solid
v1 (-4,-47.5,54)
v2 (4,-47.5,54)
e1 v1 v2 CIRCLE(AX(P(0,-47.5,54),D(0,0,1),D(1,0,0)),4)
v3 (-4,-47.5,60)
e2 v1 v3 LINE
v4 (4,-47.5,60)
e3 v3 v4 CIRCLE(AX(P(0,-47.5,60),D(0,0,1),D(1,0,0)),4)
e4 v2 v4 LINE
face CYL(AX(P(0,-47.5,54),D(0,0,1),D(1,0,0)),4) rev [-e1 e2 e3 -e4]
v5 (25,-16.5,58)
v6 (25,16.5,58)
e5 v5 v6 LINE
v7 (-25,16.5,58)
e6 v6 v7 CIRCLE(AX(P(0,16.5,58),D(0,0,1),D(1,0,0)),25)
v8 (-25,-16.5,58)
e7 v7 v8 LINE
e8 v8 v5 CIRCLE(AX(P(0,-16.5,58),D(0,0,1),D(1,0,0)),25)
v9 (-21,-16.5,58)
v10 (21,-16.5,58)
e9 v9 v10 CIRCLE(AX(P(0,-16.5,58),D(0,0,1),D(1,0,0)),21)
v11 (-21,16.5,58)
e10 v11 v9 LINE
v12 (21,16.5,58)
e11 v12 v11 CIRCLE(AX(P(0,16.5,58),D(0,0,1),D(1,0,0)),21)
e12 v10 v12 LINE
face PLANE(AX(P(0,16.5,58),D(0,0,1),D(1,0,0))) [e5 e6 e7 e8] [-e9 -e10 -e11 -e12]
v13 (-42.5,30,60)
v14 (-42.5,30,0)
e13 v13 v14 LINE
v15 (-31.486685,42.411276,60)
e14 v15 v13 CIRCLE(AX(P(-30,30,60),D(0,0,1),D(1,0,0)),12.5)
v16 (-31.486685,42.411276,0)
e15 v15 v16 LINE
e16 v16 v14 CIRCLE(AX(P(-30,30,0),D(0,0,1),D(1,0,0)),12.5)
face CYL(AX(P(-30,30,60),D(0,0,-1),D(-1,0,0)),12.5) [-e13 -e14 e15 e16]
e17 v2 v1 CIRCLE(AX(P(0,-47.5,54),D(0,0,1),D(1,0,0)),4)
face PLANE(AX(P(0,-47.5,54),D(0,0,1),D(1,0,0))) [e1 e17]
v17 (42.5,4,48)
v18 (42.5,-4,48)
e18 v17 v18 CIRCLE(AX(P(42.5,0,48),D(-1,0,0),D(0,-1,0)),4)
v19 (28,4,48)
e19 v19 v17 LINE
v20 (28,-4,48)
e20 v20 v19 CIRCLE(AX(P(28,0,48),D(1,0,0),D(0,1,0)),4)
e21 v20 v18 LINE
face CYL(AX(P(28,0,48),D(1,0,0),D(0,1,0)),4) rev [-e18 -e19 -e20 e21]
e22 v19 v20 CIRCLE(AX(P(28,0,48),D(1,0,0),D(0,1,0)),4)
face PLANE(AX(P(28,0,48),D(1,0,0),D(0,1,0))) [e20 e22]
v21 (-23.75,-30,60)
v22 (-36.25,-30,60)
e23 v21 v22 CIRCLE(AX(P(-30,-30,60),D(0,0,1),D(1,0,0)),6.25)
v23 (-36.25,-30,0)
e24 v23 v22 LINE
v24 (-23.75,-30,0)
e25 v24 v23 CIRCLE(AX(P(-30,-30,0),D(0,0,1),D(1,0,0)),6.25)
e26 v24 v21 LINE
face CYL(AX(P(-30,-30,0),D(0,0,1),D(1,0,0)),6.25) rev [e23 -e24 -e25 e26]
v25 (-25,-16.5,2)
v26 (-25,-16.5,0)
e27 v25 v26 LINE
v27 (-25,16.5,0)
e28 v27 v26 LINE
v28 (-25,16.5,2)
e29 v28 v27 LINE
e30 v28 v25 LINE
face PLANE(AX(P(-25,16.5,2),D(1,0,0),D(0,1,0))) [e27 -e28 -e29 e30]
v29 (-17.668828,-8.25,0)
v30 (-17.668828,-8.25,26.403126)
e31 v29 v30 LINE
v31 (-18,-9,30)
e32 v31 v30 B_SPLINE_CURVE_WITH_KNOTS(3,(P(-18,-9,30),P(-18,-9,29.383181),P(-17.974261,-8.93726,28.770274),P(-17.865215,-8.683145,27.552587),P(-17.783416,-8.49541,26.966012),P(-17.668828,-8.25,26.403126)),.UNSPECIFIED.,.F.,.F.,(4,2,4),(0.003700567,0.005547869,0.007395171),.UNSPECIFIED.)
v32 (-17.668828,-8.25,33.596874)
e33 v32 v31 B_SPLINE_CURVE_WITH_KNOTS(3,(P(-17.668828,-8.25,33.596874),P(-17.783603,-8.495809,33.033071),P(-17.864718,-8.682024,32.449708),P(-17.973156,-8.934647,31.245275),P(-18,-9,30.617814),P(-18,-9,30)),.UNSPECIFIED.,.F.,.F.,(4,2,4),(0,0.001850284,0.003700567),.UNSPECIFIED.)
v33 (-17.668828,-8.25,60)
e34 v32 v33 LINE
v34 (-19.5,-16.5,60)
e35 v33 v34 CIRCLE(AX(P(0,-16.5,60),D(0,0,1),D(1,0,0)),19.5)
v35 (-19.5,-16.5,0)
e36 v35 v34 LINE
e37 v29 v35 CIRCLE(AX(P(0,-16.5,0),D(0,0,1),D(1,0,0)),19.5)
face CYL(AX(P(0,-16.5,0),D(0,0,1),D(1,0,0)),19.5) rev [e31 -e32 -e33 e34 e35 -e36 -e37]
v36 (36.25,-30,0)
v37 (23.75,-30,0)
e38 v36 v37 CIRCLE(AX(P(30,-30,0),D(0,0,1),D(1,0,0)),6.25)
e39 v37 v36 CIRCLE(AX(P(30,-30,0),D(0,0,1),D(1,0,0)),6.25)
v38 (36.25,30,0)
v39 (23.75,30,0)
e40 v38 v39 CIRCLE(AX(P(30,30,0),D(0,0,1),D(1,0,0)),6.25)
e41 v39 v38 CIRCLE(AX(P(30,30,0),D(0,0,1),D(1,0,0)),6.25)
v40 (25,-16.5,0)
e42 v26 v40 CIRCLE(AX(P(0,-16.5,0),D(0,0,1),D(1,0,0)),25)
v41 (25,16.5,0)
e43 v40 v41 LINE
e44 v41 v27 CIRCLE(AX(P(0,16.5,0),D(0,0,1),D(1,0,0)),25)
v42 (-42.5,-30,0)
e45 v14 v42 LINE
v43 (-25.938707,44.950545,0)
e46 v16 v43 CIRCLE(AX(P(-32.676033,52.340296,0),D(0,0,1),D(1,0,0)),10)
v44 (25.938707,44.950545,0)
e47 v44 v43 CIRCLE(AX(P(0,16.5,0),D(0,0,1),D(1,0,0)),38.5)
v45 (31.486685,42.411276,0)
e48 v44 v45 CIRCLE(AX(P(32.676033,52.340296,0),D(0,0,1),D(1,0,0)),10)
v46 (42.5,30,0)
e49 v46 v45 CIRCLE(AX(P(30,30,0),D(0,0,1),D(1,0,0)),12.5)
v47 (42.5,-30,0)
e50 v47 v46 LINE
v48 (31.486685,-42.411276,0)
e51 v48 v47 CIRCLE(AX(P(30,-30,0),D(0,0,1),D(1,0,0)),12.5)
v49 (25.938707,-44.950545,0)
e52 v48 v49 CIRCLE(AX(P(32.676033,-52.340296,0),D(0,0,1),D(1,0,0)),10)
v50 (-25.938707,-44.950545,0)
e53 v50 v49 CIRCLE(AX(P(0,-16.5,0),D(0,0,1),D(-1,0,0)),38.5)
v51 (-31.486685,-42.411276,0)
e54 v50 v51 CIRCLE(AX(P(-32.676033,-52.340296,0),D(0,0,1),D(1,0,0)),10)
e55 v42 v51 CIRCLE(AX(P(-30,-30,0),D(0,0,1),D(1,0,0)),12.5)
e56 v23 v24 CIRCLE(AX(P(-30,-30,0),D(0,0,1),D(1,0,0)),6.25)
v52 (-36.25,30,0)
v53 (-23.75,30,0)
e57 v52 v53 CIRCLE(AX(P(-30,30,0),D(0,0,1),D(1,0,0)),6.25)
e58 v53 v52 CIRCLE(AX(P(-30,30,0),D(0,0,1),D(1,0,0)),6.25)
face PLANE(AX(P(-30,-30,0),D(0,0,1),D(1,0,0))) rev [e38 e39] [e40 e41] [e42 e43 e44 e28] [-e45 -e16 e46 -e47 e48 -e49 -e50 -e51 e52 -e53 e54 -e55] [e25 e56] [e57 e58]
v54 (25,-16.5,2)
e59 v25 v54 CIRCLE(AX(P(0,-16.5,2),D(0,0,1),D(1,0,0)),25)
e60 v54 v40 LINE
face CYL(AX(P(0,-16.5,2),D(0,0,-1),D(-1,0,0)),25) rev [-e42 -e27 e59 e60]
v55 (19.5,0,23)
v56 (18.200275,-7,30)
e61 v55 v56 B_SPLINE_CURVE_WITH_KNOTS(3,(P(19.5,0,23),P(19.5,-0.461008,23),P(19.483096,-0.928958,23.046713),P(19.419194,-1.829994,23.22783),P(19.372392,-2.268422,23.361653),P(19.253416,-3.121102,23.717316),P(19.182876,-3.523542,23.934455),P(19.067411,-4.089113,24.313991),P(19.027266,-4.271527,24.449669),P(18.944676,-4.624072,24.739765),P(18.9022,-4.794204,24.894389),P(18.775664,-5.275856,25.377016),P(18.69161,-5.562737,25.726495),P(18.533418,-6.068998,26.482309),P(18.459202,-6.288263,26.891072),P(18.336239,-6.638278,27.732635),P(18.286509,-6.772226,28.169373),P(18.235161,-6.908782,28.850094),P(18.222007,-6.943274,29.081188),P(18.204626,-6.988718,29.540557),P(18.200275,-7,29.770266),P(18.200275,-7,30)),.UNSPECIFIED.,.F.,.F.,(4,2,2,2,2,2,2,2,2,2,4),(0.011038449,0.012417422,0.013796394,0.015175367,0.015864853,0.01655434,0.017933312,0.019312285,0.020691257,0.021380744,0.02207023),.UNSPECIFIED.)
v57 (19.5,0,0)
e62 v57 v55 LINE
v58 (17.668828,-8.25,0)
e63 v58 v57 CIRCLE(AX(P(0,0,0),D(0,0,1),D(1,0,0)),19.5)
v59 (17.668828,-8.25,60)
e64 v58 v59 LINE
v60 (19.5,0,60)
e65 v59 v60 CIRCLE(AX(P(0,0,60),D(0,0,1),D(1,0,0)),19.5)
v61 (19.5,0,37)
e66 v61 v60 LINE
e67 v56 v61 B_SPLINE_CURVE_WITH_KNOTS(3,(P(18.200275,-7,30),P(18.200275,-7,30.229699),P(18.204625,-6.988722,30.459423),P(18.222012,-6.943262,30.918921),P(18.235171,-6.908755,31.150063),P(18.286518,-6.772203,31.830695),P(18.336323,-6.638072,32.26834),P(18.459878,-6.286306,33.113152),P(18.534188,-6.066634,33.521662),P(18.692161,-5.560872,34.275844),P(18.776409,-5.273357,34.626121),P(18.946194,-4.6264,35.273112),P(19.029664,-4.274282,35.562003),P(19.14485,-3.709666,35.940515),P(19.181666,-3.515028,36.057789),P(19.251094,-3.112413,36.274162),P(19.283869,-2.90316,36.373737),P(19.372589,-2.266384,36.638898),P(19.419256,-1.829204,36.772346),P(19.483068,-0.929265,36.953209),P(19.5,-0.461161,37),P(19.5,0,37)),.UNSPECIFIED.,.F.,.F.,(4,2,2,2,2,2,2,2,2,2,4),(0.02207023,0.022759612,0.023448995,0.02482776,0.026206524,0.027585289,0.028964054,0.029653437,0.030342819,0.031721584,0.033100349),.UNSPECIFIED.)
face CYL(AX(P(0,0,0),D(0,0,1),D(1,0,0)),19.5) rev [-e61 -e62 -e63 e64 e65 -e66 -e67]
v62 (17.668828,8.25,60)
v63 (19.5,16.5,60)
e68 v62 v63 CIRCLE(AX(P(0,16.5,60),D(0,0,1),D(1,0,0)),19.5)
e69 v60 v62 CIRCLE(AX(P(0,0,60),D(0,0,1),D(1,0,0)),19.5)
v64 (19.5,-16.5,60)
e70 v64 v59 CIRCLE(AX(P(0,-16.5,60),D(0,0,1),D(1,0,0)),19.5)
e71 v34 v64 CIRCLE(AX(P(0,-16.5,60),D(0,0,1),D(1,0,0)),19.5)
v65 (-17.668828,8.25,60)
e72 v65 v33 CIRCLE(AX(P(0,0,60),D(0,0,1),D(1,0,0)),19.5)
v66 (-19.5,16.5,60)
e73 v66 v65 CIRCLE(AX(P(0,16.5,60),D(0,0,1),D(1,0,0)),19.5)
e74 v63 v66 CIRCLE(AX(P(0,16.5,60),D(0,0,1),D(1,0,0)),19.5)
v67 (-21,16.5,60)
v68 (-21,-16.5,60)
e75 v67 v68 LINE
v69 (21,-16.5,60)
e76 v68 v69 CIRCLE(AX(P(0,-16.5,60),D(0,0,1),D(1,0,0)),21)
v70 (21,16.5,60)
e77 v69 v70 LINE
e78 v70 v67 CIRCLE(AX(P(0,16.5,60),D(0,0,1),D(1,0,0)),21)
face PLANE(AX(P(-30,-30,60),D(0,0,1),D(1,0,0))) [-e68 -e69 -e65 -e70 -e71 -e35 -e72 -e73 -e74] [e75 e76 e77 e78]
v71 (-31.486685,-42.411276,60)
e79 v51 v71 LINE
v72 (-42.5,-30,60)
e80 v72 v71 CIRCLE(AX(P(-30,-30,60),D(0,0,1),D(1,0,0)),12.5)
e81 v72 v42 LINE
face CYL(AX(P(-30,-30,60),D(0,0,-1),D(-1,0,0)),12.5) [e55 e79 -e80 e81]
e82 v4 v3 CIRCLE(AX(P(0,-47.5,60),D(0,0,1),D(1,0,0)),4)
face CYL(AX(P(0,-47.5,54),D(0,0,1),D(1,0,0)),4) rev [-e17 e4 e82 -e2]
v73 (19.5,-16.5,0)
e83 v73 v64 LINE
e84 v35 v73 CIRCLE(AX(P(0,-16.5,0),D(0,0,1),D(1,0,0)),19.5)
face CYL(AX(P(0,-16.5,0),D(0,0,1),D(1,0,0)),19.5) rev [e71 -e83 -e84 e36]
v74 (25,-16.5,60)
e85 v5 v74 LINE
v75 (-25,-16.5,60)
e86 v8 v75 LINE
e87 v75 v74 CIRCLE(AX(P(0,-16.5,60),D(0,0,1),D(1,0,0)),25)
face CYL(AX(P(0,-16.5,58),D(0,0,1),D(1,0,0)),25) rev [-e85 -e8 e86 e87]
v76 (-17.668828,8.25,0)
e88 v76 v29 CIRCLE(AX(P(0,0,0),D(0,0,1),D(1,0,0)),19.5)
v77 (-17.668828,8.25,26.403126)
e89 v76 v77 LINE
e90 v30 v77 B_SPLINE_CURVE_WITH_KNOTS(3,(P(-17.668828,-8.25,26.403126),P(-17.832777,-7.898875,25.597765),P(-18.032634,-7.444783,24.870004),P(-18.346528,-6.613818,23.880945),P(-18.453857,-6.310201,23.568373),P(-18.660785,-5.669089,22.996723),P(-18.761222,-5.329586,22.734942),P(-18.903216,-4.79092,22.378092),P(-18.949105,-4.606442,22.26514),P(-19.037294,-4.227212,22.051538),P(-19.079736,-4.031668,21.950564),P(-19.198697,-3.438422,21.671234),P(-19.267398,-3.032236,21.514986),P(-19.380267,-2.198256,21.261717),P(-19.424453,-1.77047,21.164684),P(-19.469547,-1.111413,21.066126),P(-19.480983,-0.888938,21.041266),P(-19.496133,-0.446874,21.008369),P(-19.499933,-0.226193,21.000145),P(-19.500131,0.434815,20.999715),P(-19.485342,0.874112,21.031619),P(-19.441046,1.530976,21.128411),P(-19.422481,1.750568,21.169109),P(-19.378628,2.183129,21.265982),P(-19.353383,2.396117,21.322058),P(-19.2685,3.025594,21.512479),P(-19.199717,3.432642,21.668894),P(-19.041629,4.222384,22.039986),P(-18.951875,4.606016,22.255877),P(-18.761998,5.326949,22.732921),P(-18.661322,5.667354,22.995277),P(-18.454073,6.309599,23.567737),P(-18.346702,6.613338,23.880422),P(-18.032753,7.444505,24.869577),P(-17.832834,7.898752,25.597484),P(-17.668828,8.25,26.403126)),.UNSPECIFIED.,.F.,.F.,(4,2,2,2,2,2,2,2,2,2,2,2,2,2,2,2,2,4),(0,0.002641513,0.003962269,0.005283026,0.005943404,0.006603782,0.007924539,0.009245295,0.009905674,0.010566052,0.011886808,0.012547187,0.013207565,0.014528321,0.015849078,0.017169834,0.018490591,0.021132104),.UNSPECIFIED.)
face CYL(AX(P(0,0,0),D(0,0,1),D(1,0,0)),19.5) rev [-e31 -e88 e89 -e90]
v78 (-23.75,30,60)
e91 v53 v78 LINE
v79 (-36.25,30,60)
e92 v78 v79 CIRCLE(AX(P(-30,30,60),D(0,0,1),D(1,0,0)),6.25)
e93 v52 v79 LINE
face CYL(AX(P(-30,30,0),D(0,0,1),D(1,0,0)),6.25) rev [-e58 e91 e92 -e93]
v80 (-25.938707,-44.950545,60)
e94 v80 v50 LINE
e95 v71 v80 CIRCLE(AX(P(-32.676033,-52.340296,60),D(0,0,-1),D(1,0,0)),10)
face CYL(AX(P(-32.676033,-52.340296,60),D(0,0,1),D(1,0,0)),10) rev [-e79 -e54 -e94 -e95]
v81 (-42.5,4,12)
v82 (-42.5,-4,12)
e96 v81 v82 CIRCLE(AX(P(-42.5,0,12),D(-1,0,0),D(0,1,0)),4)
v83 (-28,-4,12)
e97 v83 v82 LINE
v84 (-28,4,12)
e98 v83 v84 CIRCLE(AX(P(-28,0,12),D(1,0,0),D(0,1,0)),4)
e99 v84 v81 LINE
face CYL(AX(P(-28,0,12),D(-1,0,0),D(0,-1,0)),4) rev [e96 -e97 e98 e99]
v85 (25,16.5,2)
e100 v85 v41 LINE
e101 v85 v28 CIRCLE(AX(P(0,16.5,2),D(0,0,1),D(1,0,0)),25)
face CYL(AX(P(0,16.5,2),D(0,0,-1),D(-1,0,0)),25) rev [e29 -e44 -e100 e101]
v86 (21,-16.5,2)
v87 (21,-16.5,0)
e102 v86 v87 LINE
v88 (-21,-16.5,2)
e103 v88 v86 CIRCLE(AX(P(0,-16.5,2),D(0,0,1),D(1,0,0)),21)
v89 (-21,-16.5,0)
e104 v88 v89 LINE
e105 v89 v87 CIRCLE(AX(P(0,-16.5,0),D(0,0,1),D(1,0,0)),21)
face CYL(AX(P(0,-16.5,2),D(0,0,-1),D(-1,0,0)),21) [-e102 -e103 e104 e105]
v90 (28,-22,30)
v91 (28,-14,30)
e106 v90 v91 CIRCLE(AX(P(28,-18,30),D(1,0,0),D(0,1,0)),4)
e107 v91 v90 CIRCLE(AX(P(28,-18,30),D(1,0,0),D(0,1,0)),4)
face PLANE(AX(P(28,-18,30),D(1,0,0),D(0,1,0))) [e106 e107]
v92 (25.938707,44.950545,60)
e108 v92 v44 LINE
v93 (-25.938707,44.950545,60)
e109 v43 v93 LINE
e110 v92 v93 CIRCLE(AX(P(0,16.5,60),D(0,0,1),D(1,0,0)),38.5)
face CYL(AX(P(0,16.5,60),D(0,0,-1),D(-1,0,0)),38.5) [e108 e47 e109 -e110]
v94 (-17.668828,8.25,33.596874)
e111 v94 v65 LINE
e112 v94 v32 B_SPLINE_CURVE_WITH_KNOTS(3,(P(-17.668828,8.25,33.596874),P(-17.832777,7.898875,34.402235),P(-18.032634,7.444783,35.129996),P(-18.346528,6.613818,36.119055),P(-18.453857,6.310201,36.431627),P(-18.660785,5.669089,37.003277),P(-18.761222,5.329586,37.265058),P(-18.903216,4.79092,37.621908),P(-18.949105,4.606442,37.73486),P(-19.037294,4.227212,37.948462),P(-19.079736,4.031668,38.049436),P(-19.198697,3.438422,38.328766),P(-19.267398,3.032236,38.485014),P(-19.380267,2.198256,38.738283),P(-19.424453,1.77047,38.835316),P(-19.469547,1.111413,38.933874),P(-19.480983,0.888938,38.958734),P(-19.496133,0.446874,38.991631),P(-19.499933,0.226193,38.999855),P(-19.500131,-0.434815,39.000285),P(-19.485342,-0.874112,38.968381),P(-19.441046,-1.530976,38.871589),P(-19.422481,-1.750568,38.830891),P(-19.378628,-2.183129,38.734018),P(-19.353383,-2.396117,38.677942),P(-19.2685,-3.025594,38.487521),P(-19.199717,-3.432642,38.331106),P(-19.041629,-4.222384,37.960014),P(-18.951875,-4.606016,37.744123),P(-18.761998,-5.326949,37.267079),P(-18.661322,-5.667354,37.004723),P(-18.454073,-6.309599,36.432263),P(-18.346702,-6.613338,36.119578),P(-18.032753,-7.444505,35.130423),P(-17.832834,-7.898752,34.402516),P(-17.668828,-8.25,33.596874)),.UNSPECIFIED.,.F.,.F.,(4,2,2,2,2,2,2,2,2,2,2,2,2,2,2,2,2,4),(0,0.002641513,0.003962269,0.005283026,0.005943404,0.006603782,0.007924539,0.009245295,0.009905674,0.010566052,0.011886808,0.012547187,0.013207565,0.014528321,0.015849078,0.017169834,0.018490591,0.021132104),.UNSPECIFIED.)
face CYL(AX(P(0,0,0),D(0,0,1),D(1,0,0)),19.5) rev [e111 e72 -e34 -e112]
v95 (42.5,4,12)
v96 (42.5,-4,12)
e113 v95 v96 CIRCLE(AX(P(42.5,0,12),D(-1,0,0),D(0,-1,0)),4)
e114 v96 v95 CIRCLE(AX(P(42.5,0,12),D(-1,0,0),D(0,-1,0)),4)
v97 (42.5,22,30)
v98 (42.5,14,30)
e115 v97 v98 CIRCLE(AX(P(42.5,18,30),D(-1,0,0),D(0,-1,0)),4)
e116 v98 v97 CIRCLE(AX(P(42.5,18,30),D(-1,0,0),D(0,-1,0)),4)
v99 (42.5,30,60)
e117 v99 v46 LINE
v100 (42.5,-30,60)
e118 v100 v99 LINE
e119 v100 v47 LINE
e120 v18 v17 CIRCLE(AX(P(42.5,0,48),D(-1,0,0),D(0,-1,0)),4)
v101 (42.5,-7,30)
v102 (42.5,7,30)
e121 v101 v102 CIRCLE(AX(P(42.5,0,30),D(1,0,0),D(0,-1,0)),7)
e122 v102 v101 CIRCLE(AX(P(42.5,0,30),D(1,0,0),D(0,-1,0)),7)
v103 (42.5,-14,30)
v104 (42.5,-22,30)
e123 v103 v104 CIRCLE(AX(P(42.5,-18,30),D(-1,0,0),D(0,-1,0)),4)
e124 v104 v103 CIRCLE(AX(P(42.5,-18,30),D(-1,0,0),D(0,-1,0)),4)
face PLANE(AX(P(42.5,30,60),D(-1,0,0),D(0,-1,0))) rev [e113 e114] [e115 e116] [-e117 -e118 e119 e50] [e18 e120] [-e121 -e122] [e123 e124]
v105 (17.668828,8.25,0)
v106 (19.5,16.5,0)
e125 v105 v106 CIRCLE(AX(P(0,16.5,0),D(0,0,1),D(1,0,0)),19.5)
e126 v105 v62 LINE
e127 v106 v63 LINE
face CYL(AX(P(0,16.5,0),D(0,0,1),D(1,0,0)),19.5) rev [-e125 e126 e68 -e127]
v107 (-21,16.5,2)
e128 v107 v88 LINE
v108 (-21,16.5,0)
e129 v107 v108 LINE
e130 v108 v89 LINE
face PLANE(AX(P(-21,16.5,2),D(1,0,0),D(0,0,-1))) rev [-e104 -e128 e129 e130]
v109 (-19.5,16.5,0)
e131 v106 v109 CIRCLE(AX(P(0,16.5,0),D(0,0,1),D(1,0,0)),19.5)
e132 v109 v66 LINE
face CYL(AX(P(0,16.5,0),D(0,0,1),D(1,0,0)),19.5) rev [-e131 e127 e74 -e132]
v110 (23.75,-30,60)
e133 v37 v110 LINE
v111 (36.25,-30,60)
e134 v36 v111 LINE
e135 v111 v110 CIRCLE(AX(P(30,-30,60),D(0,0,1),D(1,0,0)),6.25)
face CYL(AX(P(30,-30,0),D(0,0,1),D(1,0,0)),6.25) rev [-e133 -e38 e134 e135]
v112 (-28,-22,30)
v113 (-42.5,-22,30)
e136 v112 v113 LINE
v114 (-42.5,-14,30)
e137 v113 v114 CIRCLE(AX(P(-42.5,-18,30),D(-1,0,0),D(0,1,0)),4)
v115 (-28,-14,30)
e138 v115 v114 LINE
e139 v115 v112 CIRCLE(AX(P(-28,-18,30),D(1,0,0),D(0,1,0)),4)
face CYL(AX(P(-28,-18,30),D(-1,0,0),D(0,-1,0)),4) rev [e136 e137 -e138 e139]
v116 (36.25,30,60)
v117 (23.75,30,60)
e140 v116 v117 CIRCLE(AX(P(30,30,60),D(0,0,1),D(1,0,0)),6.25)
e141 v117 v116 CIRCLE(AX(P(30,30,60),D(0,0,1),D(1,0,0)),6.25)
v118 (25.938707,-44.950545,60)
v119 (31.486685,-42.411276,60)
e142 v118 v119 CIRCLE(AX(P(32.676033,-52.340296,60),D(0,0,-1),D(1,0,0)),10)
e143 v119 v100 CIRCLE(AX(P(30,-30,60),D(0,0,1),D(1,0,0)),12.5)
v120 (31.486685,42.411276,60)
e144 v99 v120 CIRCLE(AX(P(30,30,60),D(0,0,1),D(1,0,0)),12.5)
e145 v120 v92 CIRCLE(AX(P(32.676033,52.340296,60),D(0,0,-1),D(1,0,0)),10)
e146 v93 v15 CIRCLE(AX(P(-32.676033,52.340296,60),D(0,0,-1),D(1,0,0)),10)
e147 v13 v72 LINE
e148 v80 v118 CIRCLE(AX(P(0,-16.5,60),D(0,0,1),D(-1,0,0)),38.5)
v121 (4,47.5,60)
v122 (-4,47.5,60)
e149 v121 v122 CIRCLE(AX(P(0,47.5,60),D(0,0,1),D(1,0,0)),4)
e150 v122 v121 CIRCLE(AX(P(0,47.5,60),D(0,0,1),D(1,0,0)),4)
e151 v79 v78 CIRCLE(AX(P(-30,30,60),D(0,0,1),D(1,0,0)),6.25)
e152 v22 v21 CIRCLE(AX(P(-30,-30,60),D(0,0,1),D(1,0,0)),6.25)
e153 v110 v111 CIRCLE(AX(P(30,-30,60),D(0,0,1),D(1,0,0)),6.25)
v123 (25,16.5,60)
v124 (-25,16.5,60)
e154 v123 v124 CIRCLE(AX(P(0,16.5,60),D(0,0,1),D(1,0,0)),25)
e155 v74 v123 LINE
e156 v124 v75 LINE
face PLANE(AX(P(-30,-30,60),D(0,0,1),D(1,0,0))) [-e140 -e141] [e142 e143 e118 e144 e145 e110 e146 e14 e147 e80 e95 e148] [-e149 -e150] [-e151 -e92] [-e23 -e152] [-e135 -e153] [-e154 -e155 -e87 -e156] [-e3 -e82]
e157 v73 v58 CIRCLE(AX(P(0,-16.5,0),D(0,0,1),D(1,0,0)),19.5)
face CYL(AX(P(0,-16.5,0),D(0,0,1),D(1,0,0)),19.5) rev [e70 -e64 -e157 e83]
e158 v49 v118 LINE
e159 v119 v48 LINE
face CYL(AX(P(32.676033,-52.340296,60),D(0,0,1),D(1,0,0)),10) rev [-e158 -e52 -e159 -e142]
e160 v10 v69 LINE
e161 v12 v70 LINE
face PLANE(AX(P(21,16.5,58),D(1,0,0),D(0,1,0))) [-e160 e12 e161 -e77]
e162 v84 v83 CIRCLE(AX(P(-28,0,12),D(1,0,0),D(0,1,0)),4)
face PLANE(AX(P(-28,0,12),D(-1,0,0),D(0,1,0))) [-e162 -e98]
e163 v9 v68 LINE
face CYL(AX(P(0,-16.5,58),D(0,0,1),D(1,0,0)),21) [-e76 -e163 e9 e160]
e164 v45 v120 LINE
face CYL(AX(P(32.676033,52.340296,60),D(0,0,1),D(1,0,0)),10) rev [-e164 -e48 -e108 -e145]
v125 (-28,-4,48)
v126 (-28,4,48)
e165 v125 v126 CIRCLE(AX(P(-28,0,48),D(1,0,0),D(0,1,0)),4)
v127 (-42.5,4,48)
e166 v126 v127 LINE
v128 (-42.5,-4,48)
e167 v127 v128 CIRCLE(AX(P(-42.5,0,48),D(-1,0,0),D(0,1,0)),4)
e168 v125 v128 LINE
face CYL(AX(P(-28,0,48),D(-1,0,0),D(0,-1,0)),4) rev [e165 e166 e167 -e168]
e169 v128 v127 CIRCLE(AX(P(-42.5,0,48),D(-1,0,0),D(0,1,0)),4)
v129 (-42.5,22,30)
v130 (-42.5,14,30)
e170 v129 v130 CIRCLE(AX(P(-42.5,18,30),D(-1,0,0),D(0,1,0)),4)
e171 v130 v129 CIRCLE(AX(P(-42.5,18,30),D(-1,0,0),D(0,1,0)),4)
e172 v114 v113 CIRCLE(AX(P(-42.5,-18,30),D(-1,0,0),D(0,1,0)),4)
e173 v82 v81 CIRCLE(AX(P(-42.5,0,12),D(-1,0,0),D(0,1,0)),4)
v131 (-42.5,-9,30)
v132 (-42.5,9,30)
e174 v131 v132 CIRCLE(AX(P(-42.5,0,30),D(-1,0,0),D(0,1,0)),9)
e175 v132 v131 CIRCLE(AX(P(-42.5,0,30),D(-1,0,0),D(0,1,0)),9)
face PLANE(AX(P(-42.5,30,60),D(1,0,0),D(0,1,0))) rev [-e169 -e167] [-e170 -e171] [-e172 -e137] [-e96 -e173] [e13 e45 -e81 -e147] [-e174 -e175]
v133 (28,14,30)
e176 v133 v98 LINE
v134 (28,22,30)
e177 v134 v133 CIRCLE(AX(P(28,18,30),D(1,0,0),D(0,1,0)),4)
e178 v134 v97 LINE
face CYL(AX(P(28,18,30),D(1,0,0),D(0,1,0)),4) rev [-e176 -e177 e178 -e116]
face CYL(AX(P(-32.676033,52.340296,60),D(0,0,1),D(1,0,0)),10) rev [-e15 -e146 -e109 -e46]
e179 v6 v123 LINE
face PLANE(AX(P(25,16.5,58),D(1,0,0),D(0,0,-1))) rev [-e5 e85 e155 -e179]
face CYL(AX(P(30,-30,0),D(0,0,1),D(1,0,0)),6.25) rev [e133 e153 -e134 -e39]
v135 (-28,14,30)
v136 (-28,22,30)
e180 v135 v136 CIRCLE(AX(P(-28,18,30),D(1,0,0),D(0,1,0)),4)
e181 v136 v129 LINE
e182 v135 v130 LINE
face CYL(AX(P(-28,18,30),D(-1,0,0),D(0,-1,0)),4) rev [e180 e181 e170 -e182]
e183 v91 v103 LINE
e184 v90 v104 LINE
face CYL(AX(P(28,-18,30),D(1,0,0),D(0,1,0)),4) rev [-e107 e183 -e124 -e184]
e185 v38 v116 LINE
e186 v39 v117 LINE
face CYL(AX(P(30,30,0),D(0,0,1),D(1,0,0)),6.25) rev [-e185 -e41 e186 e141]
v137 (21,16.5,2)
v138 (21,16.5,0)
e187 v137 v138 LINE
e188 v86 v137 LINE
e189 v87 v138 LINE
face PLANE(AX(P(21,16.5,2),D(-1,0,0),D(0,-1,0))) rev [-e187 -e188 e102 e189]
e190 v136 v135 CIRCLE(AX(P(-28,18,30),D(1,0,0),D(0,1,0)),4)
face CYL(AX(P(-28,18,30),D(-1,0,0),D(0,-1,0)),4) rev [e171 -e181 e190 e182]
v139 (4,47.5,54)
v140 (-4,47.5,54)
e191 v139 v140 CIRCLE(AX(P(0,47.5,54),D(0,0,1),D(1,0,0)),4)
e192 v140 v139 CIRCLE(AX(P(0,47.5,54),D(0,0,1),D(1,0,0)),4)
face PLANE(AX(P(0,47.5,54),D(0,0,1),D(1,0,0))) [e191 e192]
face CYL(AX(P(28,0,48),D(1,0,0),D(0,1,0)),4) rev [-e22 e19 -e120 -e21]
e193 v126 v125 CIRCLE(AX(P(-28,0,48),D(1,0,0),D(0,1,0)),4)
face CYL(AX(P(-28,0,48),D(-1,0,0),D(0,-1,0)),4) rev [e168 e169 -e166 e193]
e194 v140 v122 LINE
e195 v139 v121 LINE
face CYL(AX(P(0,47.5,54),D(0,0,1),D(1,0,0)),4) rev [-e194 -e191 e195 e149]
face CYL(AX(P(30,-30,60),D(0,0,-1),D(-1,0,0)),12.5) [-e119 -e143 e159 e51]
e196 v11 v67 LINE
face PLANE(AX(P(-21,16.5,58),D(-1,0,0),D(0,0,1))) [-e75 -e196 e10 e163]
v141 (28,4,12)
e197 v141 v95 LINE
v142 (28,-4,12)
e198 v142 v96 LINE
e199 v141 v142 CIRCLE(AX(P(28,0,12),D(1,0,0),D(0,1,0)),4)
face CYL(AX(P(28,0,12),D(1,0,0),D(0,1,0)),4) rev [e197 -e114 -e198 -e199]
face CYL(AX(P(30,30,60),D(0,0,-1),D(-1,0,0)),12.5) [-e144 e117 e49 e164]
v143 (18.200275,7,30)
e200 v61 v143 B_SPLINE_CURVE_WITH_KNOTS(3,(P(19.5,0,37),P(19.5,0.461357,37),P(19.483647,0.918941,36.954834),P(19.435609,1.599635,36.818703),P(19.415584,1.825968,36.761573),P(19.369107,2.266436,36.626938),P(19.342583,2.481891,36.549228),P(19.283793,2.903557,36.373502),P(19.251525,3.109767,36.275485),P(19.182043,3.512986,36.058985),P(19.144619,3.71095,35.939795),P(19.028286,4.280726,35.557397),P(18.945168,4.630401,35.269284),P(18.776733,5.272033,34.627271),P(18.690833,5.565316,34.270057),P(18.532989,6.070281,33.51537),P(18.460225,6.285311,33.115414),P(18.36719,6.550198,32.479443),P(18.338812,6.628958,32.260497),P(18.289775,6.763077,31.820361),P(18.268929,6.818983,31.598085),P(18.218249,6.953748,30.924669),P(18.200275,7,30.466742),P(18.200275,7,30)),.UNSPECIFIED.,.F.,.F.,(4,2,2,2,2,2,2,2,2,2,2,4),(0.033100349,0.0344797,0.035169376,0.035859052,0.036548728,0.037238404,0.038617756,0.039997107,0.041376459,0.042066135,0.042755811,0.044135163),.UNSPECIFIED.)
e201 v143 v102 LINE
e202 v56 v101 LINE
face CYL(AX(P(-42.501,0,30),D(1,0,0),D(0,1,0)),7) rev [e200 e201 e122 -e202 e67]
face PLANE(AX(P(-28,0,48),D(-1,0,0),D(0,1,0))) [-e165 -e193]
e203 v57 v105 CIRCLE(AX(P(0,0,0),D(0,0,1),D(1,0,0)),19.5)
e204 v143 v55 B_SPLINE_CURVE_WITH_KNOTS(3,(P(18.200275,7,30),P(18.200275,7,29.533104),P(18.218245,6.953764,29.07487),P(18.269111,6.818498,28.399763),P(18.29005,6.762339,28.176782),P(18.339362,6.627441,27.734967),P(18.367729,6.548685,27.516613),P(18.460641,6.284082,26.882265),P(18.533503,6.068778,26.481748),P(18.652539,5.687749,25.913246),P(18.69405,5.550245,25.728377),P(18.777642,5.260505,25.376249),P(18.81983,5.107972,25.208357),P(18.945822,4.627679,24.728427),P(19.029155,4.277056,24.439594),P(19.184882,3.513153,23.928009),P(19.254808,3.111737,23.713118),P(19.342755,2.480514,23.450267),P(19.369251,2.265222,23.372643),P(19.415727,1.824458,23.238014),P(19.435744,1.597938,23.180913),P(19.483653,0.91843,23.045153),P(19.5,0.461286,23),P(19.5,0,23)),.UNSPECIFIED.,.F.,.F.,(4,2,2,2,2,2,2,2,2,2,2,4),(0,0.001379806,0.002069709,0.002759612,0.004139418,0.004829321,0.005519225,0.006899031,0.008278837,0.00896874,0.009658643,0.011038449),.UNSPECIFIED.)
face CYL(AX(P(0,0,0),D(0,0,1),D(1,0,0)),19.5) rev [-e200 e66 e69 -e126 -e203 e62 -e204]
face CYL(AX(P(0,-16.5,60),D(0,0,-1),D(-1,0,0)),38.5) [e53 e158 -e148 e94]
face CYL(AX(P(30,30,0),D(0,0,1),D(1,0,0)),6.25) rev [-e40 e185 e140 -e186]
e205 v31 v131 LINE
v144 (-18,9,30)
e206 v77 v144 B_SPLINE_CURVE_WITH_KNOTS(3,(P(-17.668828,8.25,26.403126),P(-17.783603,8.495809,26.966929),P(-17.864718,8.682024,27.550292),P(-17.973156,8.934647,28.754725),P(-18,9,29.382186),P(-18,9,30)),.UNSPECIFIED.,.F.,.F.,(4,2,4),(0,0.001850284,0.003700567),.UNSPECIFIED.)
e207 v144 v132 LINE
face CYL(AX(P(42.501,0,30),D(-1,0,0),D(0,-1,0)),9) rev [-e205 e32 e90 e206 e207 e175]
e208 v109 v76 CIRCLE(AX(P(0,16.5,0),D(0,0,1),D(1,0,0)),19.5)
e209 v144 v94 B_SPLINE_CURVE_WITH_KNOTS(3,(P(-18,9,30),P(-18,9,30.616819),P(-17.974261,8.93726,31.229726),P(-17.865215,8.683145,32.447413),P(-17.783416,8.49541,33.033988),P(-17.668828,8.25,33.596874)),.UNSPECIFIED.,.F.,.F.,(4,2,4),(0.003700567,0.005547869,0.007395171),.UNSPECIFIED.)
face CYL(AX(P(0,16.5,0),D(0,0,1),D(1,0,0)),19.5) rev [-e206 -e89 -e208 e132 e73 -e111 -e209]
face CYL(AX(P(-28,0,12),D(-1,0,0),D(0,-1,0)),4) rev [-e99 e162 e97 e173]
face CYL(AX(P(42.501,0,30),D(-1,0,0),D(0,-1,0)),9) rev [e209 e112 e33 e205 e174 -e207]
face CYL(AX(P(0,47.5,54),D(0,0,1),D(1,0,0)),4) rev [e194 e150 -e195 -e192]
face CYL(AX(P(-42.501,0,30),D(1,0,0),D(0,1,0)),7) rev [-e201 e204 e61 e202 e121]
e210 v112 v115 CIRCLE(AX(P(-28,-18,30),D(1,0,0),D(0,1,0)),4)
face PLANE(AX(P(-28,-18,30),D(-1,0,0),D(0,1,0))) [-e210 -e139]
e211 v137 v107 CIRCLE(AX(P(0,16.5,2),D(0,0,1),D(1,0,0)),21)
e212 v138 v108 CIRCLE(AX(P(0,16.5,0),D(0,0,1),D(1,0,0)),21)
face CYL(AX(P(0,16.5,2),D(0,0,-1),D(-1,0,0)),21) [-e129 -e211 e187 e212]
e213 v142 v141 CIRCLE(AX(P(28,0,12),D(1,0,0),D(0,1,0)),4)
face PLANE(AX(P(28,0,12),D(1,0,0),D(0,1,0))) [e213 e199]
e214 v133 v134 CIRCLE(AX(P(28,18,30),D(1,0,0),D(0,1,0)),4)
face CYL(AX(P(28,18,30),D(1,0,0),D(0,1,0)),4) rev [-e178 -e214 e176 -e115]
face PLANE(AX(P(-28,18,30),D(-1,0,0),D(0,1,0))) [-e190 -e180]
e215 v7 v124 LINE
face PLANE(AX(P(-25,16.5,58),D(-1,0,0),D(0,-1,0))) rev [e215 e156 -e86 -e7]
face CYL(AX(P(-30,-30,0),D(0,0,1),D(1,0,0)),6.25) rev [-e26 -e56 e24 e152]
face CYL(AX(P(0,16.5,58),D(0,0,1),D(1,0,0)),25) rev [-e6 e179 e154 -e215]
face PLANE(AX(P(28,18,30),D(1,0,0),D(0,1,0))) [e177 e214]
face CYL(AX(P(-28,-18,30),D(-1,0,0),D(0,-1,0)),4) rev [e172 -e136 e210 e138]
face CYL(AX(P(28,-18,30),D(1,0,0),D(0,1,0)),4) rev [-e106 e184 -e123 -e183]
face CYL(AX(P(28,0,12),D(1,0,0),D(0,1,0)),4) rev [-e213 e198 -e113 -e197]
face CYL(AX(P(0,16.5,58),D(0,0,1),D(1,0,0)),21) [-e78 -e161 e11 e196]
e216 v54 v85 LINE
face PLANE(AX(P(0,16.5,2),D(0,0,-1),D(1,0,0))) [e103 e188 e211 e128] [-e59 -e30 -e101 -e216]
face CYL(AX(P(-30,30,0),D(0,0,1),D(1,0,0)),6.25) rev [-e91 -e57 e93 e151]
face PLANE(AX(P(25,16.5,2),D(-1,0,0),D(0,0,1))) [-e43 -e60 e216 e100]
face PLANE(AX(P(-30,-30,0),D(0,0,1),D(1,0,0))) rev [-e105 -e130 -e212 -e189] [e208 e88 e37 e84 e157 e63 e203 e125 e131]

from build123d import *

# Parameters (mm, degrees)
EXTRUDE_1_DEPTH          = 60
SKETCH_3_R               = 6.25
CUT_EXTRUDE_1_DEPTH      = 92.821838361
CUT_EXTRUDE_2_DEPTH      = 92.821838361
CUT_EXTRUDE_3_DEPTH      = 2
SKETCH_6_R               = 4
CUT_EXTRUDE_4_DEPTH      = 6
CUT_EXTRUDE_5_REACH      = 120.048
CUT_EXTRUDE_5_END_RADIUS = 19.5
SKETCH_10_R              = 7
CUT_EXTRUDE_6_REACH      = 120.048
SKETCH_11_R              = 9
SKETCH_7_R               = 4
CUT_EXTRUDE_7_DEPTH      = 15
FILLET_1_R               = 10


with BuildPart() as part:
    # 草图2 → 凸台-拉伸1 (new body)
    with BuildSketch(Plane.XY):
        with BuildLine():
            Line((-42.5, 30), (-42.5, -30))
            ThreePointArc((-42.5, -30), (-38.283749789, -39.36106241), (-28.479281689, -42.407151801))
            ThreePointArc((-28.479281689, -42.407151801), (0, -55), (28.479281689, -42.407151801))
            ThreePointArc((28.479281689, -42.407151801), (38.283749789, -39.36106241), (42.5, -30))
            Line((42.5, -30), (42.5, 30))
            ThreePointArc((42.5, 30), (38.283749789, 39.36106241), (28.479281689, 42.407151801))
            ThreePointArc((28.479281689, 42.407151801), (0, 55), (-28.479281689, 42.407151801))
            ThreePointArc((-28.479281689, 42.407151801), (-38.283749789, 39.36106241), (-42.5, 30))
        make_face()
    extrude(amount=EXTRUDE_1_DEPTH)

    # 草图3 → 切除-拉伸1 (cut, through all)
    with BuildSketch(Plane.XY.offset(60)):
        with Locations((-30, 30)):
            Circle(SKETCH_3_R)
        with Locations((30, 30)):
            Circle(SKETCH_3_R)
        with Locations((-30, -30)):
            Circle(SKETCH_3_R)
        with Locations((30, -30)):
            Circle(SKETCH_3_R)
    extrude(amount=-CUT_EXTRUDE_1_DEPTH, mode=Mode.SUBTRACT)

    # 草图4 → 切除-拉伸2 (cut, through all)
    with BuildSketch(Plane.XY.offset(60)):
        with BuildLine():
            ThreePointArc((17.668828484, 8.25), (0, 36), (-17.668828484, 8.25))
            ThreePointArc((-17.668828484, 8.25), (-19.5, 0), (-17.668828484, -8.25))
            ThreePointArc((-17.668828484, -8.25), (0, -36), (17.668828484, -8.25))
            ThreePointArc((17.668828484, -8.25), (19.5, 0), (17.668828484, 8.25))
        make_face()
    extrude(amount=-CUT_EXTRUDE_2_DEPTH, mode=Mode.SUBTRACT)

    # 草图5 → 切除-拉伸3 (cut)
    with BuildSketch(Plane.XY.offset(60)):
        with BuildLine():
            Line((-25, 16.5), (-25, -16.5))
            ThreePointArc((-25, -16.5), (0, -41.5), (25, -16.5))
            Line((25, -16.5), (25, 16.5))
            ThreePointArc((25, 16.5), (0, 41.5), (-25, 16.5))
        make_face()
        with BuildLine():
            Line((-21, 16.5), (-21, -16.5))
            ThreePointArc((-21, -16.5), (0, -37.5), (21, -16.5))
            Line((21, -16.5), (21, 16.5))
            ThreePointArc((21, 16.5), (0, 37.5), (-21, 16.5))
        make_face(mode=Mode.SUBTRACT)
    cut_extrude_3 = extrude(amount=-CUT_EXTRUDE_3_DEPTH, mode=Mode.SUBTRACT)

    # 草图6 → 切除-拉伸4 (cut)
    with BuildSketch(Plane.XY.offset(60)):
        with Locations((0, 47.5)):
            Circle(SKETCH_6_R)
        with Locations((0, -47.5)):
            Circle(SKETCH_6_R)
    extrude(amount=-CUT_EXTRUDE_4_DEPTH, mode=Mode.SUBTRACT)

    # 镜向1: 切除-拉伸3 across plane
    add(cut_extrude_3.mirror(Plane.XY.offset(30)), mode=Mode.SUBTRACT)

    # 切除-拉伸5: up to this cylinder (the profile starts outside it)
    cut_extrude_5_end = Plane(origin=(0, 0, 30), z_dir=(0, 0, 1)) * Cylinder(CUT_EXTRUDE_5_END_RADIUS, 280.096, mode=Mode.PRIVATE)
    # 草图10 → 切除-拉伸5 (cut, up to the surface)
    with BuildSketch(Plane(origin=(43, 0, 0), x_dir=(0, 0, -1), z_dir=(1, 0, 0)), mode=Mode.PRIVATE) as cut_extrude_5_sk1:
        with Locations(Location((-30, 0, 0), (0, 0, 90))):
            Circle(SKETCH_10_R)
    cut_extrude_5_tool1 = extrude(cut_extrude_5_sk1.sketch, amount=-CUT_EXTRUDE_5_REACH, mode=Mode.PRIVATE) - cut_extrude_5_end
    add(cut_extrude_5_tool1.solids().sort_by_distance((43, 0, 30))[0], mode=Mode.SUBTRACT)

    # 草图11 → 切除-拉伸6 (cut, up to next)
    with BuildSketch(Plane.ZY.offset(43), mode=Mode.PRIVATE) as cut_extrude_6_sk1:
        with Locations(Location((30, 0, 0), (0, 0, 246.443535691))):
            Circle(SKETCH_11_R)
    cut_extrude_6_tool1 = extrude(cut_extrude_6_sk1.sketch, amount=-CUT_EXTRUDE_6_REACH, mode=Mode.PRIVATE) & part.part
    add(cut_extrude_6_tool1.solids().sort_by_distance((-43, 0, 30))[0], mode=Mode.SUBTRACT)

    # 草图7 → 切除-拉伸7 (cut)
    with BuildSketch(Plane(origin=(43, 0, 0), x_dir=(0, 0, -1), z_dir=(1, 0, 0))):
        with Locations(Location((-30, 18, 0), (0, 0, 90))):
            Circle(SKETCH_7_R)
        with Locations(Location((-48, 0, 0), (0, 0, 90))):
            Circle(SKETCH_7_R)
        with Locations(Location((-30, -18, 0), (0, 0, 90))):
            Circle(SKETCH_7_R)
        with Locations(Location((-12, 0, 0), (0, 0, 90))):
            Circle(SKETCH_7_R)
    cut_extrude_7 = extrude(amount=-CUT_EXTRUDE_7_DEPTH, mode=Mode.SUBTRACT)

    # 镜向2: 切除-拉伸7 across plane
    add(cut_extrude_7.mirror(Plane(origin=(0, 0, 0), x_dir=(0, 0, 1), z_dir=(1, 0, 0))), mode=Mode.SUBTRACT)

    # 圆角1
    fillet_1_edges = [part.edges().sort_by_distance(p)[0] for p in [
        (-28.479281689, 42.407151801, 30),
        (28.479281689, 42.407151801, 30),
        (28.479281689, -42.407151801, 30),
        (-28.479281689, -42.407151801, 30),
    ]]
    fillet(fillet_1_edges, radius=FILLET_1_R)


solid = part.part
